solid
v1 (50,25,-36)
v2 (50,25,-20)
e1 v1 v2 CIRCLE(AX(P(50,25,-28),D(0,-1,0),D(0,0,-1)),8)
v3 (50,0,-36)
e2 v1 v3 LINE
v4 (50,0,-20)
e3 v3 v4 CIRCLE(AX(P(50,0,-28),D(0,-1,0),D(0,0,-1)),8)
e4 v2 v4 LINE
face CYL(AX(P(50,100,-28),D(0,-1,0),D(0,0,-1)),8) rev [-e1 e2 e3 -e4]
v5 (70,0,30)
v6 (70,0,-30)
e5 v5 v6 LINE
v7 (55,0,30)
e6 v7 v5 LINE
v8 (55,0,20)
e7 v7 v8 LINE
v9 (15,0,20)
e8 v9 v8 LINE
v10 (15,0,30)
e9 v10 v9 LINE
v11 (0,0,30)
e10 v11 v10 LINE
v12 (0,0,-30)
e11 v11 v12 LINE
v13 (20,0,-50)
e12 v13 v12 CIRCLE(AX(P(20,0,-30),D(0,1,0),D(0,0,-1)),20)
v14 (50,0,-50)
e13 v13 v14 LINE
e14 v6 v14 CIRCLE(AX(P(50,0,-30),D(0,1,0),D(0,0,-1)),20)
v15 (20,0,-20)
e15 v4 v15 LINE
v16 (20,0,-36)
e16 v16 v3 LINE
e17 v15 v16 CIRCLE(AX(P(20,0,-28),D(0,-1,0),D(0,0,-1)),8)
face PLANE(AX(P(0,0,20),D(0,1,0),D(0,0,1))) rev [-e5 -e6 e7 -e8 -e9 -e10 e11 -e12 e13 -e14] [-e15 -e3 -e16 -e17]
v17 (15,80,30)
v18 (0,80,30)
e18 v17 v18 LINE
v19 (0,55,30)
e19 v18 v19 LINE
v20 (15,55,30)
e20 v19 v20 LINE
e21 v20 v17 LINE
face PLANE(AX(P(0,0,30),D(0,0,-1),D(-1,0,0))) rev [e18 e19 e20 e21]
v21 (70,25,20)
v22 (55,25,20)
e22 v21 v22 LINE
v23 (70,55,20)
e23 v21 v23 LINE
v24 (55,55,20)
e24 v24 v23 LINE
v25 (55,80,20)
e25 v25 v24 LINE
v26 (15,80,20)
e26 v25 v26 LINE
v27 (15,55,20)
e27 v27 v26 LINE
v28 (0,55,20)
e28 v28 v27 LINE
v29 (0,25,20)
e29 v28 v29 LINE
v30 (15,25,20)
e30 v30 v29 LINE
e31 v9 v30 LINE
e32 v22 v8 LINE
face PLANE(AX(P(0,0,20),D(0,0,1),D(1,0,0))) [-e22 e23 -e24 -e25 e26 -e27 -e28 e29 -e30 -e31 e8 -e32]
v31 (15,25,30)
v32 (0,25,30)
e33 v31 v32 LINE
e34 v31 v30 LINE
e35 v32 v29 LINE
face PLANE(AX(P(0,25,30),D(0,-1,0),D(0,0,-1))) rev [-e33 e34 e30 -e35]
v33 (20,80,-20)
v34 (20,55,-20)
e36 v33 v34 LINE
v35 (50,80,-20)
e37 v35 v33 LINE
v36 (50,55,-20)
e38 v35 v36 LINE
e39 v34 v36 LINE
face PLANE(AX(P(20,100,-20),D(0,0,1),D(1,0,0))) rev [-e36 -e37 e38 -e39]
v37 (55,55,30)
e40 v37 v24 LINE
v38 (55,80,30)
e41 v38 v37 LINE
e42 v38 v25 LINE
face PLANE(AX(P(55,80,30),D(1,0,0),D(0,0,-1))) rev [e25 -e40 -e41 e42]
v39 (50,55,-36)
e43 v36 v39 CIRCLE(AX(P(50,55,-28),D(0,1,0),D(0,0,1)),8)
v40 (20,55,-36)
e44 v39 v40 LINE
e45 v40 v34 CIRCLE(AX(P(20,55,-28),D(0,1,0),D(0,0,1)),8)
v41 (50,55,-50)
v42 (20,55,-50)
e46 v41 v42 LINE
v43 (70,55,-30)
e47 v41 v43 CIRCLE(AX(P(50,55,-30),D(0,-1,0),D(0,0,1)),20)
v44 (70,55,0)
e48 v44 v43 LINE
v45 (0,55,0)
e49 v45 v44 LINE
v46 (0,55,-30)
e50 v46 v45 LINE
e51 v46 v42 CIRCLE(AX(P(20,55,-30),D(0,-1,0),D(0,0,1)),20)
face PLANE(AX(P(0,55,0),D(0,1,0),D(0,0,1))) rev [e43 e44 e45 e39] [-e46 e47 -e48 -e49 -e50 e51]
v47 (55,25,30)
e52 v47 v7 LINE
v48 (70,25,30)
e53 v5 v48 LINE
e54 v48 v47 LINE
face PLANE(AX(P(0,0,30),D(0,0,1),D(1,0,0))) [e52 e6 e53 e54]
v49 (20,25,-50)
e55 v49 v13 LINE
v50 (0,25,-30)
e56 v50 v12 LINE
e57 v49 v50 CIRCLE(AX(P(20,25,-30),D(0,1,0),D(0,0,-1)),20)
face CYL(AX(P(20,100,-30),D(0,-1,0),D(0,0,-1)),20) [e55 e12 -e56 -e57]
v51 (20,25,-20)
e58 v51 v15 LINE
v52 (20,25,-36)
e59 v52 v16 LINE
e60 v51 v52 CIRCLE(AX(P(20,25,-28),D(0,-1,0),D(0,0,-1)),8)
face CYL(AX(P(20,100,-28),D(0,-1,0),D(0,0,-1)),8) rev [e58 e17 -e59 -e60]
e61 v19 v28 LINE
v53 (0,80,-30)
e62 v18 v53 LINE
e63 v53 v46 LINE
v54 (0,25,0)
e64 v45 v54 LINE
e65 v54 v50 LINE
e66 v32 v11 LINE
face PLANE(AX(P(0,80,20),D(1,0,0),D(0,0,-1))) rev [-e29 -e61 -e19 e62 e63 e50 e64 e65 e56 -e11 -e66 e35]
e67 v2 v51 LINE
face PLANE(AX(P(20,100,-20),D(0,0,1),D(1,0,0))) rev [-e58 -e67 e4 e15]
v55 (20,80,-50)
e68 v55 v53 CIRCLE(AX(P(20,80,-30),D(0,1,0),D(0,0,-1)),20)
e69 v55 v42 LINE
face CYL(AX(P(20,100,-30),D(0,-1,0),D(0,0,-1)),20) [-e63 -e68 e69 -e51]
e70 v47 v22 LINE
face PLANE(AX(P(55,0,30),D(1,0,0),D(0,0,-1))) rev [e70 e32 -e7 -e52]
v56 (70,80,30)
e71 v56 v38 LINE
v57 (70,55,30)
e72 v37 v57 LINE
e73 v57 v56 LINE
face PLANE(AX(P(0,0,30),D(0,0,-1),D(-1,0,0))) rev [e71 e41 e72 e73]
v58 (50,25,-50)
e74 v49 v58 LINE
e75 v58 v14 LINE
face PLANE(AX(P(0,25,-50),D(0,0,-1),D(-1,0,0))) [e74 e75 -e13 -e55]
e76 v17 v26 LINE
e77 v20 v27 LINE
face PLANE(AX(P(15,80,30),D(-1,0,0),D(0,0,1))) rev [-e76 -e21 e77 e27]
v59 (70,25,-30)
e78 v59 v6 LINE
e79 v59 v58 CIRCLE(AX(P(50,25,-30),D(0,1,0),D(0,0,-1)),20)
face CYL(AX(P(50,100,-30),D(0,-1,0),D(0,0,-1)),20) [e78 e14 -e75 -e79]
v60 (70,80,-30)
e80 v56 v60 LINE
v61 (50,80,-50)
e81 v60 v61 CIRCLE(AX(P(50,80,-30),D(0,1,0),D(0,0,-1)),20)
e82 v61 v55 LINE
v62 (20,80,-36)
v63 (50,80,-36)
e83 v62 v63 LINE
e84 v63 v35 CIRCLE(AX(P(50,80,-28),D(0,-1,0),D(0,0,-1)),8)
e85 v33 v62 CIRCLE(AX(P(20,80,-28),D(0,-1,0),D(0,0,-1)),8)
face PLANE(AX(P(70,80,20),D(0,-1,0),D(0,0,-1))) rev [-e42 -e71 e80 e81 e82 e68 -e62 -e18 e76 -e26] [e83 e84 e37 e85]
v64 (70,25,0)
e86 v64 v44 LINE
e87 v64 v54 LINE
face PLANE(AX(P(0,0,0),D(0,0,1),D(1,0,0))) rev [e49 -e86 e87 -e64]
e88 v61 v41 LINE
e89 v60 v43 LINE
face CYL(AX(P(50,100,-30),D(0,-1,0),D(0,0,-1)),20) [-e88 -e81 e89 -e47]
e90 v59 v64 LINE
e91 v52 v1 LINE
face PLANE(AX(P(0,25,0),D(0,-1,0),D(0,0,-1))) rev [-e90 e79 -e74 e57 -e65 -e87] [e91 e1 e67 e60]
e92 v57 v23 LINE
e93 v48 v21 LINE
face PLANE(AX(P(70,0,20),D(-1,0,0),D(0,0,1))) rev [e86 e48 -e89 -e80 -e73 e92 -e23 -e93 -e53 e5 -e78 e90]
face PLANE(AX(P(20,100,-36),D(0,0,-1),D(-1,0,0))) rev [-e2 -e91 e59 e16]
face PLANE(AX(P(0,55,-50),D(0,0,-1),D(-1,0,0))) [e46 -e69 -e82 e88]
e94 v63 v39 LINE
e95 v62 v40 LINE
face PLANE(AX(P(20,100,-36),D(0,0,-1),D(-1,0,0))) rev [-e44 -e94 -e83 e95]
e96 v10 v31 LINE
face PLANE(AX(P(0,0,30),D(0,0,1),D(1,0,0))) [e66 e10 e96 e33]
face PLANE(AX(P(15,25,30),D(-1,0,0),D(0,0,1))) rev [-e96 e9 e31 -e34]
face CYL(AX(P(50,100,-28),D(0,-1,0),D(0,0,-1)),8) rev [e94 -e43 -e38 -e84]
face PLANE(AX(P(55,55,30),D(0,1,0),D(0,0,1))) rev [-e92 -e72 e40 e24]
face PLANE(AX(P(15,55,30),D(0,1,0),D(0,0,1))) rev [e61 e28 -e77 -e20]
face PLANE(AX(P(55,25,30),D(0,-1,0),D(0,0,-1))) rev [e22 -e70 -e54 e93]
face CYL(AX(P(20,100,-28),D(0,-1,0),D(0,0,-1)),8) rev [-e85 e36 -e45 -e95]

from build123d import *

# Parameters (mm, degrees)
BASE_BLOCK_PROFILE_W           = 70
BASE_BLOCK_PROFILE_H           = 80
BASE_BLOCK_20MM_DEPTH          = 20
H_BOSS_PROFILE_W               = 15
H_BOSS_PROFILE_H               = 25
H_BOSS_10MM_DEPTH              = 10
REAR_BOSS_PROFILE_W            = 70
REAR_BOSS_PROFILE_H            = 50
REAR_BOSS_25MM_DEPTH           = 25
REAR_BOSS_EXTENSION_PROFILE_W  = 70
REAR_BOSS_EXTENSION_PROFILE_H  = 50
REAR_BOSS_EXTENSION_25MM_DEPTH = 25
THROUGH_SLOT_8X30_DEPTH        = 100
LOWER_NOTCH_CUT_DEPTH          = 100


with BuildPart() as part:
    # Base Block Profile → Base Block 20mm (new body)
    with BuildSketch(Plane.XY):
        with Locations((35, 40)):
            Rectangle(BASE_BLOCK_PROFILE_W, BASE_BLOCK_PROFILE_H)
    extrude(amount=BASE_BLOCK_20MM_DEPTH)

    # H Boss Profile → H Boss 10mm (add)
    with BuildSketch(Plane.XY.offset(20)):
        with Locations((7.5, 67.5)):
            Rectangle(H_BOSS_PROFILE_W, H_BOSS_PROFILE_H)
        with Locations((62.5, 67.5)):
            Rectangle(H_BOSS_PROFILE_W, H_BOSS_PROFILE_H)
        with Locations((7.5, 12.5)):
            Rectangle(H_BOSS_PROFILE_W, H_BOSS_PROFILE_H)
        with Locations((62.5, 12.5)):
            Rectangle(H_BOSS_PROFILE_W, H_BOSS_PROFILE_H)
    extrude(amount=H_BOSS_10MM_DEPTH)

    # Rear Boss Profile → Rear Boss 25mm (add)
    with BuildSketch(Plane(origin=(0, 80, 0), x_dir=(1, 0, 0), z_dir=(0, 1, 0))):
        with Locations((35, 25)):
            Rectangle(REAR_BOSS_PROFILE_W, REAR_BOSS_PROFILE_H)
    extrude(amount=-REAR_BOSS_25MM_DEPTH)

    # Rear Boss Extension Profile → Rear Boss Extension 25mm (add)
    with BuildSketch(Plane.XZ):
        with Locations((35, -25)):
            Rectangle(REAR_BOSS_EXTENSION_PROFILE_W, REAR_BOSS_EXTENSION_PROFILE_H)
    extrude(amount=-REAR_BOSS_EXTENSION_25MM_DEPTH)

    # Slot 8x30 Profile → Through Slot 8x30 (cut)
    with BuildSketch(Plane.XZ):
        with BuildLine():
            Line((20, -20), (50, -20))
            ThreePointArc((50, -20), (58, -28), (50, -36))
            Line((50, -36), (20, -36))
            ThreePointArc((20, -36), (12, -28), (20, -20))
        make_face()
    extrude(amount=-THROUGH_SLOT_8X30_DEPTH, mode=Mode.SUBTRACT)

    # Lower Notch Profile → Lower Notch Cut (cut)
    with BuildSketch(Plane.XZ):
        with BuildLine():
            Line((0, -50), (0, -30))
            ThreePointArc((0, -30), (5.857864376, -44.142135624), (20, -50))
            Line((20, -50), (0, -50))
        make_face()
        with BuildLine():
            Line((70, -50), (70, -30))
            ThreePointArc((70, -30), (64.142135624, -44.142135624), (50, -50))
            Line((50, -50), (70, -50))
        make_face()
    extrude(amount=-LOWER_NOTCH_CUT_DEPTH, mode=Mode.SUBTRACT)


solid = part.part
